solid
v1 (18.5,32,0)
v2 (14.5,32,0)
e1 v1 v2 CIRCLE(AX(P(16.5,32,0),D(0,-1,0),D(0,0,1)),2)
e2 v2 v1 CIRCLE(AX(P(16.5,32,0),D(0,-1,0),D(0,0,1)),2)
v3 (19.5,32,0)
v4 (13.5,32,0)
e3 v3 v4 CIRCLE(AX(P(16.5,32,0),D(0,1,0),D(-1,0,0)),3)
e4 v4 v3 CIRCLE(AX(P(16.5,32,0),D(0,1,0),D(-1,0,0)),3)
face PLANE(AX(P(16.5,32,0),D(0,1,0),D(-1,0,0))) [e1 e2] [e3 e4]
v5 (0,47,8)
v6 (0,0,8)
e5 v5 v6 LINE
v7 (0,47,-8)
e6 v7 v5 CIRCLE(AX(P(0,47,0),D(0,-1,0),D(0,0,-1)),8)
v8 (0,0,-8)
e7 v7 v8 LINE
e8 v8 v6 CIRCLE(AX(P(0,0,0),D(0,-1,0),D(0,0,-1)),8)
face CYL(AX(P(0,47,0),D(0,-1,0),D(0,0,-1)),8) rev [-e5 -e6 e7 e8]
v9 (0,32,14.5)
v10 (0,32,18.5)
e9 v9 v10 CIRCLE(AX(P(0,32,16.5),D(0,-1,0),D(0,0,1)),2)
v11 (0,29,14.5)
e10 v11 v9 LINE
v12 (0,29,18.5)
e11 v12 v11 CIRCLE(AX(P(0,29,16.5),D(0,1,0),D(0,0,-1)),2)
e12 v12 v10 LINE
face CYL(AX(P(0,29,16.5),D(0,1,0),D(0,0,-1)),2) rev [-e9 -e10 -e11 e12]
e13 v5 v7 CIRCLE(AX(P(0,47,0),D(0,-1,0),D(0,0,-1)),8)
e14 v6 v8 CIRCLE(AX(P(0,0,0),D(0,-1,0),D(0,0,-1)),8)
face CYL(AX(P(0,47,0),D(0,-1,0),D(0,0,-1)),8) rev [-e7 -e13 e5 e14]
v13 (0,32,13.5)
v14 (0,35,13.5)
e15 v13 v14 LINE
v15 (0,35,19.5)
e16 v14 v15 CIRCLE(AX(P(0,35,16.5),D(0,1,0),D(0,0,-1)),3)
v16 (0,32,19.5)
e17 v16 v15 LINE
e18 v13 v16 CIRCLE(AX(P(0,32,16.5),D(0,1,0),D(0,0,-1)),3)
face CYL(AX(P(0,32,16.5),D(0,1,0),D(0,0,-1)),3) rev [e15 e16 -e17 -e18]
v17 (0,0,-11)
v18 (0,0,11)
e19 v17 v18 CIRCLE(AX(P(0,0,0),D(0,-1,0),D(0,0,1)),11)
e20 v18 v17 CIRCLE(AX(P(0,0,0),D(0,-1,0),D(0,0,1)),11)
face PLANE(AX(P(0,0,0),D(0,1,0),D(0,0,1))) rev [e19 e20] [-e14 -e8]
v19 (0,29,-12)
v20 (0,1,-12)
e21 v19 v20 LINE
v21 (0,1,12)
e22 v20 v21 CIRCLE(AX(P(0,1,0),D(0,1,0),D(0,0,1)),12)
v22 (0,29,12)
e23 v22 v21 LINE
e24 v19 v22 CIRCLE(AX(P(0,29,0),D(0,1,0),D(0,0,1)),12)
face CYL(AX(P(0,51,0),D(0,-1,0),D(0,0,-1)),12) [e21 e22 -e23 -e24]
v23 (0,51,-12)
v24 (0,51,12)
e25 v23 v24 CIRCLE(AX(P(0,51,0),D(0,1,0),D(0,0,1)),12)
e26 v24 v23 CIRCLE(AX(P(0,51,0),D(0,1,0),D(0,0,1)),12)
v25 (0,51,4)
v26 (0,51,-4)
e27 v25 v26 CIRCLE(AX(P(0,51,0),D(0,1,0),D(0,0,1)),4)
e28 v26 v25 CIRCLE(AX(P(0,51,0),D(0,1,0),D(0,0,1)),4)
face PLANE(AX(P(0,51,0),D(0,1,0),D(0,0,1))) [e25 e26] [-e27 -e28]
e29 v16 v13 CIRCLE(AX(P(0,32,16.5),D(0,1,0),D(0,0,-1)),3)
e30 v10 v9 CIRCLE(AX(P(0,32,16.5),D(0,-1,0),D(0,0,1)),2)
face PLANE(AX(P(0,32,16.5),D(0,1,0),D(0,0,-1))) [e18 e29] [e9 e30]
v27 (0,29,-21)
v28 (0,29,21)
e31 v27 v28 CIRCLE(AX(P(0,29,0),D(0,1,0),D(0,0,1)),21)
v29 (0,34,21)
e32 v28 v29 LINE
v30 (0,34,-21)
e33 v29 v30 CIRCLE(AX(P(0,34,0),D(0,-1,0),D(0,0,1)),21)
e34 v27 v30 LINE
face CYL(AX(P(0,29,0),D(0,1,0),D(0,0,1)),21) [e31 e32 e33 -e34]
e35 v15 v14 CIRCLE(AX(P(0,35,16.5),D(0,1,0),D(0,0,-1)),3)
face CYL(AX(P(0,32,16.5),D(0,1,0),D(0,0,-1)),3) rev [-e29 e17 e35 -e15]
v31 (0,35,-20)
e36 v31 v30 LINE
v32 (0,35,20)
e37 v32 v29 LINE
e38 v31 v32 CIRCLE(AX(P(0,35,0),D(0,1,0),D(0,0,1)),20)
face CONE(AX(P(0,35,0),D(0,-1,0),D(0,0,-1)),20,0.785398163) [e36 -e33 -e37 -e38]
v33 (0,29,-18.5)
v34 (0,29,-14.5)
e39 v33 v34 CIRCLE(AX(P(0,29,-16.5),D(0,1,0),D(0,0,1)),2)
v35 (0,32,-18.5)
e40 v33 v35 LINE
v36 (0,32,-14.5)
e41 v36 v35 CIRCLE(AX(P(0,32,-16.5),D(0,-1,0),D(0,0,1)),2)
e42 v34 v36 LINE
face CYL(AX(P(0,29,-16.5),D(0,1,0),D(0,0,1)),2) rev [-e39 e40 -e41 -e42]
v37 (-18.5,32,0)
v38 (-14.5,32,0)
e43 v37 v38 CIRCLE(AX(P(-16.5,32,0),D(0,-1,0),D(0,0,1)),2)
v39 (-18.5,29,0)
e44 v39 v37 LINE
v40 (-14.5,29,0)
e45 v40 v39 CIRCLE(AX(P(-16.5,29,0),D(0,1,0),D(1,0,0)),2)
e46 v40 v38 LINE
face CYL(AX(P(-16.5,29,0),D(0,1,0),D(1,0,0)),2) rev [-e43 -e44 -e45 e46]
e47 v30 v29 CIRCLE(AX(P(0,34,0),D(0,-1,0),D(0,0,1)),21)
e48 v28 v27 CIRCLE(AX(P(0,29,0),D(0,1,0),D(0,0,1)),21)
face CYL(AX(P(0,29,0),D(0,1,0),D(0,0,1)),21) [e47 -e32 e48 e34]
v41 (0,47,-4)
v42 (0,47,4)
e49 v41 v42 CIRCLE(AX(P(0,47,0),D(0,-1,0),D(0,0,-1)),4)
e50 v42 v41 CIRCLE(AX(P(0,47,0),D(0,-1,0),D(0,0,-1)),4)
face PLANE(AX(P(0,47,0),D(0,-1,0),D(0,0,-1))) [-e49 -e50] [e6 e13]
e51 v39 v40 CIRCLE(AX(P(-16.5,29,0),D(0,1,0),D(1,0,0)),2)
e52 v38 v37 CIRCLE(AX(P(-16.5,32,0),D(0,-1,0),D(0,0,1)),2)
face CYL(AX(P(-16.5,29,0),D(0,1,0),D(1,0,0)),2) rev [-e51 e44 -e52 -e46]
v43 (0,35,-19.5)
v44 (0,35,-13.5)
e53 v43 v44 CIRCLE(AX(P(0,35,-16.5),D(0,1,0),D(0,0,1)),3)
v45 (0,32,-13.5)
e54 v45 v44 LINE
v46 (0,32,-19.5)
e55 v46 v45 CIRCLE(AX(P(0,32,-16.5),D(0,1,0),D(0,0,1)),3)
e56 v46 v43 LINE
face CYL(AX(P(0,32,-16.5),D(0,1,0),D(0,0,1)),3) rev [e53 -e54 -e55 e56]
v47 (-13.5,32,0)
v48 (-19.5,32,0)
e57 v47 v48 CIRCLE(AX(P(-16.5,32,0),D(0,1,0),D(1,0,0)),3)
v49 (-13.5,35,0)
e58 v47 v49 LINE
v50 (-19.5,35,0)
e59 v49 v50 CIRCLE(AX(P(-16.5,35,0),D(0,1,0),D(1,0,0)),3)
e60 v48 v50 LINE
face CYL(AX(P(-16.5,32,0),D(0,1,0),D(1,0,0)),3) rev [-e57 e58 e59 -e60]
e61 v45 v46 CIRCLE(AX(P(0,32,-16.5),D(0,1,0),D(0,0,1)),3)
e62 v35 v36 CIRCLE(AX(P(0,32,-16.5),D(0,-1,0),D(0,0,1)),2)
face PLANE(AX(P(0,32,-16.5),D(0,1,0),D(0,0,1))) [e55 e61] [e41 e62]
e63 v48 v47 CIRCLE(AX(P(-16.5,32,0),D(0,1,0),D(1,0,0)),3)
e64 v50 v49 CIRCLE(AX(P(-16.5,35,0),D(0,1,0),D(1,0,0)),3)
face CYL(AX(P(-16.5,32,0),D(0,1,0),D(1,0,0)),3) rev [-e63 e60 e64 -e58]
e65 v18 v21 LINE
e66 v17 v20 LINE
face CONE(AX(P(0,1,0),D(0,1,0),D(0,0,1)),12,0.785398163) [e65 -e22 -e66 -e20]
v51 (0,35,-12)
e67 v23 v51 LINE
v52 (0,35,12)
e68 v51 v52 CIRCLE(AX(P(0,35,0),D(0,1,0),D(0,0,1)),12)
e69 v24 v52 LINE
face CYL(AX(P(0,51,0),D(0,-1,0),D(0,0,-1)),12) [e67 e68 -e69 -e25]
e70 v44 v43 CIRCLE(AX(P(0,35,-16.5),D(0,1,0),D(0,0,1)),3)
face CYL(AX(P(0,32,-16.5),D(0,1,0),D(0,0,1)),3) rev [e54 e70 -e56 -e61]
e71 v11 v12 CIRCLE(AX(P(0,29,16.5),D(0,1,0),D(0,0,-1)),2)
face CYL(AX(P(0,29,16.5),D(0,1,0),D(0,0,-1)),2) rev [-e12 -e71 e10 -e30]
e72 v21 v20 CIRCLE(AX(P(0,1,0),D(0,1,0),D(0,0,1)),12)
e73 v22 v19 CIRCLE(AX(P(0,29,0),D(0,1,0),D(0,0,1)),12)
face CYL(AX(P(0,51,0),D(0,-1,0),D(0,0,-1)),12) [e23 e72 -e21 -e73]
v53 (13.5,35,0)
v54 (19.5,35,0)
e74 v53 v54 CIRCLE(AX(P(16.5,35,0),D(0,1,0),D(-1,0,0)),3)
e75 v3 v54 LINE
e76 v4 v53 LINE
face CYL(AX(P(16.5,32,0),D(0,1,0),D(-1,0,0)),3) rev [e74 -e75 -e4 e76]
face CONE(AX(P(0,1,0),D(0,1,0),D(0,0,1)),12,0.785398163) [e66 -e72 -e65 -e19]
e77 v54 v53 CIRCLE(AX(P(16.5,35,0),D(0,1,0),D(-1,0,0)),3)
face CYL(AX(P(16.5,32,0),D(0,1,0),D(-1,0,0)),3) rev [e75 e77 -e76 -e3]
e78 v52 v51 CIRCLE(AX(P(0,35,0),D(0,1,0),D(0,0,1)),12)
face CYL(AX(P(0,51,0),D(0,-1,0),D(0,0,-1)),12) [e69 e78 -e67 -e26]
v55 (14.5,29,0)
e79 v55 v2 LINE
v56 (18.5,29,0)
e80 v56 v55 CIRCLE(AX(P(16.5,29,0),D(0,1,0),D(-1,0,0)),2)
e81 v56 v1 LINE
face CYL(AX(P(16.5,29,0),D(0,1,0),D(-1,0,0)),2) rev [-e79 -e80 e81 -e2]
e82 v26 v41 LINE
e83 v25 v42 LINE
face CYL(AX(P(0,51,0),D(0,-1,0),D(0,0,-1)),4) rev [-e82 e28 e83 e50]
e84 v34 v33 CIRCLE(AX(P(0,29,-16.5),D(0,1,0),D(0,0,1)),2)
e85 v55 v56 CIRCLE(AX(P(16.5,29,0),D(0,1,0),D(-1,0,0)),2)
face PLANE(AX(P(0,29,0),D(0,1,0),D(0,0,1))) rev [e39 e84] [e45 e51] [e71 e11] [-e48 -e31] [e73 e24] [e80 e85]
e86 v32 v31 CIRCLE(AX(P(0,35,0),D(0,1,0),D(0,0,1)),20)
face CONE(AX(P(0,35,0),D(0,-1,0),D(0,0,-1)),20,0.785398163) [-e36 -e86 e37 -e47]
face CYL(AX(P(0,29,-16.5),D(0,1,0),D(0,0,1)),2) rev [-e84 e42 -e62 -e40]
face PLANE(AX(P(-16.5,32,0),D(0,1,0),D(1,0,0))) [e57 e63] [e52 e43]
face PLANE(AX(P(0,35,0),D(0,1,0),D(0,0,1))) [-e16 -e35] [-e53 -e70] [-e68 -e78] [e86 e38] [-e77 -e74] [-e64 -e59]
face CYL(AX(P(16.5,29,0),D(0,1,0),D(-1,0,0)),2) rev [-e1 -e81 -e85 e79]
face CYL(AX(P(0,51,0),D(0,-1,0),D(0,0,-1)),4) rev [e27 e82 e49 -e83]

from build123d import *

# Parameters (mm, degrees)
SKETCH1_R           = 12
SKETCH1_R_2         = 4
BOSS_EXTRUDE1_DEPTH = 51
SKETCH2_R           = 8
CUT_EXTRUDE1_DEPTH  = 47
BOSS_EXTRUDE2_START = -6
SKETCH3_R           = 21
SKETCH3_R_2         = 12
BOSS_EXTRUDE2_DEPTH = 6
SKETCH4_R           = 2
CUT_EXTRUDE2_DEPTH  = 6
SKETCH5_R           = 3
CUT_EXTRUDE3_DEPTH  = 3
CIRPATTERN1_COUNT   = 4
CHAMFER1_SIZE       = 1


with BuildPart() as part:
    # Sketch1 → Boss-Extrude1 (new body)
    with BuildSketch(Plane(origin=(0, 0, 0), x_dir=(1, 0, 0), z_dir=(0, 1, 0))):
        with Locations(Location((0, 0, 0), (0, 0, 270))):
            Circle(SKETCH1_R)
        with Locations(Location((0, 0, 0), (0, 0, 270))):
            Circle(SKETCH1_R_2, mode=Mode.SUBTRACT)
    extrude(amount=BOSS_EXTRUDE1_DEPTH)

    # Sketch2 → Cut-Extrude1 (cut)
    with BuildSketch(Plane.XZ):
        with Locations(Location((0, 0, 0), (0, 0, 270))):
            Circle(SKETCH2_R)
    extrude(amount=-CUT_EXTRUDE1_DEPTH, mode=Mode.SUBTRACT)

    # Sketch3 → Boss-Extrude2 (add)
    with BuildSketch(Plane(origin=(0, 35, 0), x_dir=(-1, 0, 0), z_dir=(0, 1, 0)).offset(BOSS_EXTRUDE2_START)):
        with Locations(Location((0, 0, 0), (0, 0, 90))):
            Circle(SKETCH3_R)
        with Locations(Location((0, 0, 0), (0, 0, 90))):
            Circle(SKETCH3_R_2, mode=Mode.SUBTRACT)
    extrude(amount=BOSS_EXTRUDE2_DEPTH)

    # Sketch4 → Cut-Extrude2 (cut)
    with BuildSketch(Plane(origin=(0, 35, 0), x_dir=(1, 0, 0), z_dir=(0, 1, 0))):
        with Locations(Location((0, 16.5, 0), (0, 0, 270))):
            Circle(SKETCH4_R)
    cut_extrude2 = extrude(amount=-CUT_EXTRUDE2_DEPTH, mode=Mode.SUBTRACT)

    # Sketch5 → Cut-Extrude3 (cut)
    with BuildSketch(Plane(origin=(0, 35, 0), x_dir=(1, 0, 0), z_dir=(0, 1, 0))):
        with Locations(Location((0, 16.5, 0), (0, 0, 270))):
            Circle(SKETCH5_R)
    cut_extrude3 = extrude(amount=-CUT_EXTRUDE3_DEPTH, mode=Mode.SUBTRACT)

    # CirPattern1: Cut-Extrude2, Cut-Extrude3 ×4 about axis
    cirpattern1_axis = Axis((0, 0, 0), (0, 1, 0))
    add([cut_extrude2.rotate(cirpattern1_axis, i * 360 / CIRPATTERN1_COUNT) for i in range(1, CIRPATTERN1_COUNT)], mode=Mode.SUBTRACT)
    add([cut_extrude3.rotate(cirpattern1_axis, i * 360 / CIRPATTERN1_COUNT) for i in range(1, CIRPATTERN1_COUNT)], mode=Mode.SUBTRACT)

    # Chamfer1
    chamfer1_edges = [part.edges().sort_by_distance(p)[0] for p in [
        (0, 35, -21),
        (0, 0, -12),
    ]]
    chamfer(chamfer1_edges, length=CHAMFER1_SIZE)


solid = part.part
